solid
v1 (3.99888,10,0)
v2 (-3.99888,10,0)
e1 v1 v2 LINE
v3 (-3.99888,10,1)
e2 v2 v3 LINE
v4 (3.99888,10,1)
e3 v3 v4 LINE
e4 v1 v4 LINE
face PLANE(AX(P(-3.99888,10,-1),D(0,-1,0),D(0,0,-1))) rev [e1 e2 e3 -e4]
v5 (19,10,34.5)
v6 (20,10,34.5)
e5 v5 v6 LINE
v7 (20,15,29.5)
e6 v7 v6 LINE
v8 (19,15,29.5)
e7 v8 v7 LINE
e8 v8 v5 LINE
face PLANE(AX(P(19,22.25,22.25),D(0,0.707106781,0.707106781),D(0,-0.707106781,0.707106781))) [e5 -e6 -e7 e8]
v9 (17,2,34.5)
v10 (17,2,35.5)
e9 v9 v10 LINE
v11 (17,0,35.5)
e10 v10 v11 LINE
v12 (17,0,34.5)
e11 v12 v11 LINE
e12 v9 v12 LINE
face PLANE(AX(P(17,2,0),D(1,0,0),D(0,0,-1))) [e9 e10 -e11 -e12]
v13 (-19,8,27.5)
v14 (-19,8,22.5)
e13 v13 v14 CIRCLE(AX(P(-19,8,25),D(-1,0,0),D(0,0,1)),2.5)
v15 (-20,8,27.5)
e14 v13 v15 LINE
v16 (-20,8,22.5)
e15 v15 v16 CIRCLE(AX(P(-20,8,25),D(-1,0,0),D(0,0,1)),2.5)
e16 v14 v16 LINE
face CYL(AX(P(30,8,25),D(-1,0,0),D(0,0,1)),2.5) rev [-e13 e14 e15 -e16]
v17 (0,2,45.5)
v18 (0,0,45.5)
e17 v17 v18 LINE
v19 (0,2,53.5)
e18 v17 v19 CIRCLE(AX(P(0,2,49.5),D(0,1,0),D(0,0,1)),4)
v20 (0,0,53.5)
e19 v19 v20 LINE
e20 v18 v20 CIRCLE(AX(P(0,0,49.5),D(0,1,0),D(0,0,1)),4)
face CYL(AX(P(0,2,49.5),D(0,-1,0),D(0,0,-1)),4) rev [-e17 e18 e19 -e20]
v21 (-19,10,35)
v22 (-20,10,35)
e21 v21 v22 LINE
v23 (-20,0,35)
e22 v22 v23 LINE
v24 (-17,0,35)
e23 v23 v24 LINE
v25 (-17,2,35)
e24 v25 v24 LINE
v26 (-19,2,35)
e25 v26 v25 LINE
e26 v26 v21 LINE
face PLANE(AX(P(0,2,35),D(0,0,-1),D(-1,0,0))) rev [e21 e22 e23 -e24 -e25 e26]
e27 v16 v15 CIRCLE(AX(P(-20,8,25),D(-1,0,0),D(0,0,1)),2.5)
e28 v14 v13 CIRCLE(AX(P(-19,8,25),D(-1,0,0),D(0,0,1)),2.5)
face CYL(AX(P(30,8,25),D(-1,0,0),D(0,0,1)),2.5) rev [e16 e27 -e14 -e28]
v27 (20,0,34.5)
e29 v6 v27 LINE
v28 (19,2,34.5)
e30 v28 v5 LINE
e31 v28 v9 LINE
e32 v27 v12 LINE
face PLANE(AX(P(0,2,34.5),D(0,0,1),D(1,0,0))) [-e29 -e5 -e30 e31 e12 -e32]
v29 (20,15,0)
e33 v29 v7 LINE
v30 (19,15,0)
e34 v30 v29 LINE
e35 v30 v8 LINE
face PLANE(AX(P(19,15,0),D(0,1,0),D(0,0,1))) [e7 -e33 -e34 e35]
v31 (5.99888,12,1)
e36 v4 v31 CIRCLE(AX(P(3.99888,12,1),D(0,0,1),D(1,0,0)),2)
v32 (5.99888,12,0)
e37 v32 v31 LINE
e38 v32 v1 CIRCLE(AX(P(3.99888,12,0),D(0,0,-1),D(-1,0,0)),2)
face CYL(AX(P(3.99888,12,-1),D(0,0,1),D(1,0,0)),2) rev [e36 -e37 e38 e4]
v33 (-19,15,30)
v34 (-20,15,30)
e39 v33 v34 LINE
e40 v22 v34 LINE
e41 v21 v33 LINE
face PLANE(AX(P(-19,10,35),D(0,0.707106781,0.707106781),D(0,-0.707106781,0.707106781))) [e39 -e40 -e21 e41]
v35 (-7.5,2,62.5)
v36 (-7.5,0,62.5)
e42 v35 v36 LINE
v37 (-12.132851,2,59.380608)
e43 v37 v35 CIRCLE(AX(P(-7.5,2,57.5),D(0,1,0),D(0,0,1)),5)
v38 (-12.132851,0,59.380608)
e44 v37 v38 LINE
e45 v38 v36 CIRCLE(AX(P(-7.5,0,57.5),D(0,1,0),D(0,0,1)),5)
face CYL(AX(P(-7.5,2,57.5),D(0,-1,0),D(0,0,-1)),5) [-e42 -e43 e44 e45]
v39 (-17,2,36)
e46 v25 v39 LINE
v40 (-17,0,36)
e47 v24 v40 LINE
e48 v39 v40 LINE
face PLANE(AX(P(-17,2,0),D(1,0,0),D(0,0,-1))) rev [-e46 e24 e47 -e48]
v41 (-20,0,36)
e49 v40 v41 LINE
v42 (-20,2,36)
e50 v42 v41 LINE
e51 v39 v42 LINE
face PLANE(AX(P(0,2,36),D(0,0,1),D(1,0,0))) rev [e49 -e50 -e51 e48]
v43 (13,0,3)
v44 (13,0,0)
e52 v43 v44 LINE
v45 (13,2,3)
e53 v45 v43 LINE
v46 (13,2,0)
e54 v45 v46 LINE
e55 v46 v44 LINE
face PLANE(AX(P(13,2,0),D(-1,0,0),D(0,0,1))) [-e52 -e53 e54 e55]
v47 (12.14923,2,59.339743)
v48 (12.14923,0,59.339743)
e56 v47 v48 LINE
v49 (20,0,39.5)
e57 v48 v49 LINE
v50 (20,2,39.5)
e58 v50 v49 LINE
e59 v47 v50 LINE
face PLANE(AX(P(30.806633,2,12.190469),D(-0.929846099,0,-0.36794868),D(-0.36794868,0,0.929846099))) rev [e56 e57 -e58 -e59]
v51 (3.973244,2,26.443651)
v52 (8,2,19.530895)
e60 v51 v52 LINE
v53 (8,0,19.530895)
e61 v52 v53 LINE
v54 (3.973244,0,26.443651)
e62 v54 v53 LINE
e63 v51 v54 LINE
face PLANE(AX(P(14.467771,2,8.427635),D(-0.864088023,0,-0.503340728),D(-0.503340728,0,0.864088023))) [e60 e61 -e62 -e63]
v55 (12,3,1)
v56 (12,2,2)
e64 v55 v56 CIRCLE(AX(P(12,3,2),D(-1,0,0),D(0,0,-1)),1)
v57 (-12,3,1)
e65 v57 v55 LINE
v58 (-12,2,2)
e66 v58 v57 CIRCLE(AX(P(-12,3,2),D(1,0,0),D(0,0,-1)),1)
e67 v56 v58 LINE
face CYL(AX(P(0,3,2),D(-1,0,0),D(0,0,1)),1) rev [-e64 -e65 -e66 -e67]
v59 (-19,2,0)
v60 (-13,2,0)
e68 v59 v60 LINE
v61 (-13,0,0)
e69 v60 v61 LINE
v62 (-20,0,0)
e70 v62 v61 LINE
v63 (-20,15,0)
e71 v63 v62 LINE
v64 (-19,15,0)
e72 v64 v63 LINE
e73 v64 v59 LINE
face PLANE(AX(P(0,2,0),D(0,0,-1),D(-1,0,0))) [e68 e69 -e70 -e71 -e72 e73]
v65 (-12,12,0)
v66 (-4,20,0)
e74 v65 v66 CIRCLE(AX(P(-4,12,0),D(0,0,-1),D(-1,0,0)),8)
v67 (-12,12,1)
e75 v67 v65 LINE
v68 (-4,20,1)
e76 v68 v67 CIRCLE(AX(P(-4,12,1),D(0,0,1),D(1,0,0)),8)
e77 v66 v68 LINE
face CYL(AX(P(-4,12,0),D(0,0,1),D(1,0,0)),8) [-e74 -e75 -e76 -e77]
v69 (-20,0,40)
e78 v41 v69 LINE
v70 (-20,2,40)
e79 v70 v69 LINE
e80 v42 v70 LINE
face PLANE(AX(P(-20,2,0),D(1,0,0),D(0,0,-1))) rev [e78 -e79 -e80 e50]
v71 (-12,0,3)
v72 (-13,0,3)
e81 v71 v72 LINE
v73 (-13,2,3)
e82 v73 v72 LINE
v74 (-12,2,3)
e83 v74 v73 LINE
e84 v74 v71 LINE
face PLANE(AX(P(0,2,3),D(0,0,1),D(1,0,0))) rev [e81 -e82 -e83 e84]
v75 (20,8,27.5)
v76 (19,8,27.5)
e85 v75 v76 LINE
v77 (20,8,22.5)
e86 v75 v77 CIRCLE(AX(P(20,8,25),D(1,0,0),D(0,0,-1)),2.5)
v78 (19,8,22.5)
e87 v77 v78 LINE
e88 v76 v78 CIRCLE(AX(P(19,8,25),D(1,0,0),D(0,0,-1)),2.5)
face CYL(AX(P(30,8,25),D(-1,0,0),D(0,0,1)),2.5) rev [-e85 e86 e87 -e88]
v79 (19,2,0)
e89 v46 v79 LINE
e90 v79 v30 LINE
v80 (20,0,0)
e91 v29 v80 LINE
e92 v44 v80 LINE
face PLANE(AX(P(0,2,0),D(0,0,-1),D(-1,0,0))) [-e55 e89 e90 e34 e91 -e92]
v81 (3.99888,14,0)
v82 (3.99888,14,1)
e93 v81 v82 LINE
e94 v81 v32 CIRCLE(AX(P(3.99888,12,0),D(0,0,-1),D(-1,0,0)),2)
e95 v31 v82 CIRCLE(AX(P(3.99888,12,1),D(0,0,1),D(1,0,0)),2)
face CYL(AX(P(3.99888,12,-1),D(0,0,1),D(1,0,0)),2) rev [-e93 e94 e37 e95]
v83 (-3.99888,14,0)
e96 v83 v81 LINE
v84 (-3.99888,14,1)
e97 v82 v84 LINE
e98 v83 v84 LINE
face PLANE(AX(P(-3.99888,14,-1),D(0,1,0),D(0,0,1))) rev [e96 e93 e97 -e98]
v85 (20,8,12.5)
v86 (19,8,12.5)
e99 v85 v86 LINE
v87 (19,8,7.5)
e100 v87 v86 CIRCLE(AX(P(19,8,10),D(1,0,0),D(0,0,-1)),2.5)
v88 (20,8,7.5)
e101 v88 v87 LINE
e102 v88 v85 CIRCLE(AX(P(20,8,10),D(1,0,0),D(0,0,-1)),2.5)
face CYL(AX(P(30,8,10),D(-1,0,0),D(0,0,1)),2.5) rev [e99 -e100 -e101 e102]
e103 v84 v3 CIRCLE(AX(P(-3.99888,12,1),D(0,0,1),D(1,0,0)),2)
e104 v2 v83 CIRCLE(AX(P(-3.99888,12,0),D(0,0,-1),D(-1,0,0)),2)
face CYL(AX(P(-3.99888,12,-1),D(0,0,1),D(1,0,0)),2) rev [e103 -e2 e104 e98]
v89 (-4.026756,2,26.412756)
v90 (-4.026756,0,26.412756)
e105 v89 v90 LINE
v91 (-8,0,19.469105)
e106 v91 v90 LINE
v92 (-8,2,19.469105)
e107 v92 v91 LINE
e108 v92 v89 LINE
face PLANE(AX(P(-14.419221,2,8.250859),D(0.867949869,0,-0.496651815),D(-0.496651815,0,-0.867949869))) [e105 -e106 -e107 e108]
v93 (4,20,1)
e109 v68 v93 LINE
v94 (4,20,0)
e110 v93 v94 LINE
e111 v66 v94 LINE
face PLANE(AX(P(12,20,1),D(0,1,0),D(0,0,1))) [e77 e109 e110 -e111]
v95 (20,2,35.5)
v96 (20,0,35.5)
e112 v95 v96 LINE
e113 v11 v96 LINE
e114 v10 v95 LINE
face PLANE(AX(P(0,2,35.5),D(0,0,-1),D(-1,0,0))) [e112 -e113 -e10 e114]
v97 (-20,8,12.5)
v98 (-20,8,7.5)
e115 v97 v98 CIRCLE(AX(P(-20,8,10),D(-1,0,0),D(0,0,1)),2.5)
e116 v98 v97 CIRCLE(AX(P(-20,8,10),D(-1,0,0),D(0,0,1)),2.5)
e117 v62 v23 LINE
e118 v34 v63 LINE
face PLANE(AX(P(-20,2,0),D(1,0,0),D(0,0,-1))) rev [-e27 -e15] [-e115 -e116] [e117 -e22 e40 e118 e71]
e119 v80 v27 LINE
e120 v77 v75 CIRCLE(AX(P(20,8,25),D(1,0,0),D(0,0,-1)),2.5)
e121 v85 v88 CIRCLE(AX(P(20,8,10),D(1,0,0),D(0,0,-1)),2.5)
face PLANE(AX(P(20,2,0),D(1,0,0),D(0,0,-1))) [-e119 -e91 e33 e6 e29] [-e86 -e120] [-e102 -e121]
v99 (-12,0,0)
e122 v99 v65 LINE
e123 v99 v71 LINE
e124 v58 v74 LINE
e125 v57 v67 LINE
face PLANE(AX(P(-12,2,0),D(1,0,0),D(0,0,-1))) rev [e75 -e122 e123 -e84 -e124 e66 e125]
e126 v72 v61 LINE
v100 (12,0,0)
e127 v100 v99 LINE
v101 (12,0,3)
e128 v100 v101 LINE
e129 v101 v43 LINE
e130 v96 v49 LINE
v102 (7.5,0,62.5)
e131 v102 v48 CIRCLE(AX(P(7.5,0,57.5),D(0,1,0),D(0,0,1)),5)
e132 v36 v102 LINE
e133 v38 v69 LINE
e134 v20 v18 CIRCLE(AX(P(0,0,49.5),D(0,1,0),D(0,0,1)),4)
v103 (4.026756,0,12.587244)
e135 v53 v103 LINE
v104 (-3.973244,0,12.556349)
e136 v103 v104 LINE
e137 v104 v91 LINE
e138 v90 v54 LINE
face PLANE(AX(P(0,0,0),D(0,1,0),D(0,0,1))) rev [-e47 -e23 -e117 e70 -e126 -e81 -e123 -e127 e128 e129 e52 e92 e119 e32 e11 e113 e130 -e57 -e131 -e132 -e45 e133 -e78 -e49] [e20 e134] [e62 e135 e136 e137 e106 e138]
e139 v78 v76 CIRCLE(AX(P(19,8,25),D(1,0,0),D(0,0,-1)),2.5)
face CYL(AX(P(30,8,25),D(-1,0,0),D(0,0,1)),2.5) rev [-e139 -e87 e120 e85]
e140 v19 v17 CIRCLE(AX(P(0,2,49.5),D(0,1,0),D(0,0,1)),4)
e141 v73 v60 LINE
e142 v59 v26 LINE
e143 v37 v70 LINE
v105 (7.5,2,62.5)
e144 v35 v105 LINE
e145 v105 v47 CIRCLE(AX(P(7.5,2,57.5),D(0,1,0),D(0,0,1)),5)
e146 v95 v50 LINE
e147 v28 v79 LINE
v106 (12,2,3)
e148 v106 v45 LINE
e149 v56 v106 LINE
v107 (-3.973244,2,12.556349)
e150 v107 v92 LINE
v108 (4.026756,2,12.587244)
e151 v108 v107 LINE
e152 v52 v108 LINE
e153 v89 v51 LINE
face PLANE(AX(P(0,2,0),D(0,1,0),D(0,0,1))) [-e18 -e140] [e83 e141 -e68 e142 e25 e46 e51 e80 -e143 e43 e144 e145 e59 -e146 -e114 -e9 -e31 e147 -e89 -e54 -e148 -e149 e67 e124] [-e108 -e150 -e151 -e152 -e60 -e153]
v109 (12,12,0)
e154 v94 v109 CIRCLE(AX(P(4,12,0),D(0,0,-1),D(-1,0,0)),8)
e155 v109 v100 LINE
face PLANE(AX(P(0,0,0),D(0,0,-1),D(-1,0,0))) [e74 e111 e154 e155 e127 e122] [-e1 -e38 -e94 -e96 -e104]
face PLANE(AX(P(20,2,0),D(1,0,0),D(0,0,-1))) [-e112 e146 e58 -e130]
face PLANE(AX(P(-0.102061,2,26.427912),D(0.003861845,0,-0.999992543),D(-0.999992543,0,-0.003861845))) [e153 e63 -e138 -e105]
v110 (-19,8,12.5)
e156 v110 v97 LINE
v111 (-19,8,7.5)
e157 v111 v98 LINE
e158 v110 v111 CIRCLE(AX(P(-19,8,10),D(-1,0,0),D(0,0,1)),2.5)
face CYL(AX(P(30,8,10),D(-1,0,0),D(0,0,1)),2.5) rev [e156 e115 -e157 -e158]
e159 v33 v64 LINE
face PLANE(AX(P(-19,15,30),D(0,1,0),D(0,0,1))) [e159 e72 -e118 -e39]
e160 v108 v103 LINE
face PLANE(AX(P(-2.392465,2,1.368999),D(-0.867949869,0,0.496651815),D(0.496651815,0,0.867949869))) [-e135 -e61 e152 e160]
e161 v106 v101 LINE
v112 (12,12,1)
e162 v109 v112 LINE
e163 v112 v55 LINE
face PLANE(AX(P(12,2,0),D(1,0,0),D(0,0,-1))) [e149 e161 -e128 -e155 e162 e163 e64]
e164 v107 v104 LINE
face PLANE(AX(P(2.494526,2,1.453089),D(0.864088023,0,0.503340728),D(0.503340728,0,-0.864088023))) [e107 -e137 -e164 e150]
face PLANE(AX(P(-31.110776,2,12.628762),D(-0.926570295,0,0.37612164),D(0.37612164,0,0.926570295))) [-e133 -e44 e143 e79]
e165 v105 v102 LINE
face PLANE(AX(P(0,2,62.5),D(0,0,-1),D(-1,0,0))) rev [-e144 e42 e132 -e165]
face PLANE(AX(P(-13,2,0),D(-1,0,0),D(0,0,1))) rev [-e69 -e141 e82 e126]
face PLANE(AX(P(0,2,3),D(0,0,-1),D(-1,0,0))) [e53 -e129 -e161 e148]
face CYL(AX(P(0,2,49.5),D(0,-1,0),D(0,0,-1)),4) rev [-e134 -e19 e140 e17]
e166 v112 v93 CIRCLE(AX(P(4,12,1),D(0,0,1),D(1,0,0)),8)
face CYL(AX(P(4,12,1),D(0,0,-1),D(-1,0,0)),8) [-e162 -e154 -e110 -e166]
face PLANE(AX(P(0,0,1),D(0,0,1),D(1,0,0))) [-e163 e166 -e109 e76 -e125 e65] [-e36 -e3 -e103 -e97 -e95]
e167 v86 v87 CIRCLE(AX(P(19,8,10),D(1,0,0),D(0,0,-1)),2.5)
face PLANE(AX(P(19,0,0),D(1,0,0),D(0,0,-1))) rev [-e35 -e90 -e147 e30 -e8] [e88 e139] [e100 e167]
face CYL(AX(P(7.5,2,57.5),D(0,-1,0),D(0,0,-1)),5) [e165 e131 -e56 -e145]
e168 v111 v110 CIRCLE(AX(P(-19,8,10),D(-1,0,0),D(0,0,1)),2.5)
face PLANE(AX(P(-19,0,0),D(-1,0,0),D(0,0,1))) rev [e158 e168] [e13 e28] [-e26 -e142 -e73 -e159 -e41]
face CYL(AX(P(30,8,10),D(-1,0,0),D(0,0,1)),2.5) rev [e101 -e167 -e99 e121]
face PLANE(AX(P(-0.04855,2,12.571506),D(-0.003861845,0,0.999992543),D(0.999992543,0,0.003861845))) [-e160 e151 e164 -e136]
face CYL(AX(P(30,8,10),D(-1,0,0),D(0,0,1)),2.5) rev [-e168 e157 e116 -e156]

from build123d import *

# Parameters (mm, degrees)
BASE_PLATE_PROFILE_R        = 4
BASE_PLATE_PROFILE_W        = 1
BASE_PLATE_PROFILE_H        = 35
BASE_PLATE_PROFILE_W_2      = 24
BASE_PLATE_PROFILE_H_2      = 1
BASE_PLATE_PROFILE_H_3      = 34.5
BASE_PLATE_2MM_DEPTH        = 2
TAB_SEAT_RECESS_SKETCH_W    = 24
TAB_SEAT_RECESS_SKETCH_H    = 2
TAB_SEAT_RECESS_0_5MM_DEPTH = 0.5
SIDE_FLANGES_SKETCH_W       = 34.5
SIDE_FLANGES_SKETCH_H       = 2
SIDE_FLANGES_DEPTH          = 1
FLANGE_EXTENSION_DEPTH      = 1
REAR_TAB_SKETCH_W           = 24
REAR_TAB_SKETCH_H           = 20
REAR_TAB_24X20_DEPTH        = 1
REAR_TAB_CORNER_ROUND_R8_R  = 8
TAB_SLOT_DEPTH              = 2
TAB_ROOT_FILLET_R1_R        = 1
FLANGE_CROSS_HOLES_SKETCH_R = 2.5
FLANGE_CROSS_HOLES_DEPTH    = 50


with BuildPart() as part:
    # Base Plate Profile → Base Plate 2mm (new body)
    # profile 1 of 4: a face of its own
    with BuildSketch(Plane(origin=(0, 0, 0), x_dir=(1, 0, 0), z_dir=(0, 1, 0))):
        with BuildLine():
            Line((-13, 0), (-19, 0))
            Line((-19, 0), (-19, -35))
            Line((-19, -35), (-17, -35))
            Line((-17, -35), (-17, -36))
            Line((-17, -36), (-20, -36))
            Line((-20, -36), (-20, -40))
            Line((-20, -40), (-12.132851477, -59.380608198))
            ThreePointArc((-12.132851477, -59.380608198), (-10.292575783, -61.647471578), (-7.5, -62.5))
            Line((-7.5, -62.5), (7.5, -62.5))
            ThreePointArc((7.5, -62.5), (10.310807979, -61.63513706), (12.149230497, -59.339743401))
            Line((12.149230497, -59.339743401), (20, -39.5))
            Line((20, -39.5), (20, -35.5))
            Line((20, -35.5), (17, -35.5))
            Line((17, -35.5), (17, -34.5))
            Line((17, -34.5), (19, -34.5))
            Line((19, -34.5), (19, 0))
            Line((19, 0), (13, 0))
            Line((13, 0), (13, -3))
            Line((13, -3), (12, -3))
            Line((12, -3), (12, -0.5))
            Line((12, -0.5), (-12, -0.5))
            Line((-12, -0.5), (-12, -3))
            Line((-12, -3), (-13, -3))
            Line((-13, -3), (-13, 0))
        make_face()
        with Locations(Location((0, -49.5, 0), (0, 0, 270))):
            Circle(BASE_PLATE_PROFILE_R, mode=Mode.SUBTRACT)
        Polygon((8, -19.530894994), (3.97324415, -26.443650727), (-4.02675585, -26.412755733), (-8, -19.469105006), (-3.97324415, -12.556349273), (4.02675585, -12.587244267), align=None, mode=Mode.SUBTRACT)
    # profile 2 of 4: a face of its own
    with BuildSketch(Plane(origin=(0, 0, 0), x_dir=(1, 0, 0), z_dir=(0, 1, 0))):
        with Locations((-19.5, -17.5)):
            Rectangle(BASE_PLATE_PROFILE_W, BASE_PLATE_PROFILE_H)
    # profile 3 of 4: a face of its own
    with BuildSketch(Plane(origin=(0, 0, 0), x_dir=(1, 0, 0), z_dir=(0, 1, 0))):
        Rectangle(BASE_PLATE_PROFILE_W_2, BASE_PLATE_PROFILE_H_2)
    # profile 4 of 4: a face of its own
    with BuildSketch(Plane(origin=(0, 0, 0), x_dir=(1, 0, 0), z_dir=(0, 1, 0))):
        with Locations((19.5, -17.25)):
            Rectangle(BASE_PLATE_PROFILE_W, BASE_PLATE_PROFILE_H_3)
    extrude(amount=BASE_PLATE_2MM_DEPTH)

    # Tab Seat Recess Sketch → Tab Seat Recess 0.5mm (cut)
    with BuildSketch(Plane(origin=(0, 0, -0.5), x_dir=(-1, 0, 0), z_dir=(0, 0, -1))):
        with Locations((0, 1)):
            Rectangle(TAB_SEAT_RECESS_SKETCH_W, TAB_SEAT_RECESS_SKETCH_H)
    extrude(amount=-TAB_SEAT_RECESS_0_5MM_DEPTH, mode=Mode.SUBTRACT)

    # Side Flanges Sketch → Side Flanges (add)
    with BuildSketch(Plane(origin=(20, 0, 0), x_dir=(0, 0, -1), z_dir=(1, 0, 0))):
        Polygon((0, 15), (-29.5, 15), (-34.5, 10), (-34.5, 2), (0, 2), align=None)
        with Locations((-17.25, 1)):
            Rectangle(SIDE_FLANGES_SKETCH_W, SIDE_FLANGES_SKETCH_H)
    extrude(amount=-SIDE_FLANGES_DEPTH)

    # Flange Extension Sketch → Flange Extension (add)
    with BuildSketch(Plane.ZY.offset(20)):
        Polygon((0, 15), (0, 0), (35, 0), (35, 10), (30, 15), align=None)
    extrude(amount=-FLANGE_EXTENSION_DEPTH)

    # Rear Tab Sketch → Rear Tab 24x20 (add)
    with BuildSketch(Plane(origin=(0, 0, 0), x_dir=(-1, 0, 0), z_dir=(0, 0, -1))):
        with Locations((0, 10)):
            Rectangle(REAR_TAB_SKETCH_W, REAR_TAB_SKETCH_H)
    extrude(amount=-REAR_TAB_24X20_DEPTH)

    # Rear Tab Corner Round R8
    rear_tab_corner_round_r8_edges = [part.edges().sort_by_distance(p)[0] for p in [
        (12, 20, 0.5),
        (-12, 20, 0.5),
    ]]
    fillet(rear_tab_corner_round_r8_edges, radius=REAR_TAB_CORNER_ROUND_R8_R)

    # Tab Slot Sketch → Tab Slot (cut)
    with BuildSketch(Plane.XY.offset(1)):
        with BuildLine():
            Line((-3.998880062, 14), (3.998880062, 14))
            ThreePointArc((3.998880062, 14), (5.998880062, 12), (3.998880062, 10))
            Line((3.998880062, 10), (-3.998880062, 10))
            ThreePointArc((-3.998880062, 10), (-5.998880062, 12), (-3.998880062, 14))
        make_face()
    extrude(amount=-TAB_SLOT_DEPTH, mode=Mode.SUBTRACT)

    # Tab Root Fillet R1
    tab_root_fillet_r1_edges = [part.edges().sort_by_distance(p)[0] for p in [
        (0, 2, 1),
    ]]
    fillet(tab_root_fillet_r1_edges, radius=TAB_ROOT_FILLET_R1_R)

    # Flange Cross Holes Sketch → Flange Cross Holes (cut)
    with BuildSketch(Plane.ZY.offset(20)):
        with Locations((10, 8)):
            Circle(FLANGE_CROSS_HOLES_SKETCH_R)
        with Locations((25, 8)):
            Circle(FLANGE_CROSS_HOLES_SKETCH_R)
    extrude(amount=-FLANGE_CROSS_HOLES_DEPTH, mode=Mode.SUBTRACT)


solid = part.part
